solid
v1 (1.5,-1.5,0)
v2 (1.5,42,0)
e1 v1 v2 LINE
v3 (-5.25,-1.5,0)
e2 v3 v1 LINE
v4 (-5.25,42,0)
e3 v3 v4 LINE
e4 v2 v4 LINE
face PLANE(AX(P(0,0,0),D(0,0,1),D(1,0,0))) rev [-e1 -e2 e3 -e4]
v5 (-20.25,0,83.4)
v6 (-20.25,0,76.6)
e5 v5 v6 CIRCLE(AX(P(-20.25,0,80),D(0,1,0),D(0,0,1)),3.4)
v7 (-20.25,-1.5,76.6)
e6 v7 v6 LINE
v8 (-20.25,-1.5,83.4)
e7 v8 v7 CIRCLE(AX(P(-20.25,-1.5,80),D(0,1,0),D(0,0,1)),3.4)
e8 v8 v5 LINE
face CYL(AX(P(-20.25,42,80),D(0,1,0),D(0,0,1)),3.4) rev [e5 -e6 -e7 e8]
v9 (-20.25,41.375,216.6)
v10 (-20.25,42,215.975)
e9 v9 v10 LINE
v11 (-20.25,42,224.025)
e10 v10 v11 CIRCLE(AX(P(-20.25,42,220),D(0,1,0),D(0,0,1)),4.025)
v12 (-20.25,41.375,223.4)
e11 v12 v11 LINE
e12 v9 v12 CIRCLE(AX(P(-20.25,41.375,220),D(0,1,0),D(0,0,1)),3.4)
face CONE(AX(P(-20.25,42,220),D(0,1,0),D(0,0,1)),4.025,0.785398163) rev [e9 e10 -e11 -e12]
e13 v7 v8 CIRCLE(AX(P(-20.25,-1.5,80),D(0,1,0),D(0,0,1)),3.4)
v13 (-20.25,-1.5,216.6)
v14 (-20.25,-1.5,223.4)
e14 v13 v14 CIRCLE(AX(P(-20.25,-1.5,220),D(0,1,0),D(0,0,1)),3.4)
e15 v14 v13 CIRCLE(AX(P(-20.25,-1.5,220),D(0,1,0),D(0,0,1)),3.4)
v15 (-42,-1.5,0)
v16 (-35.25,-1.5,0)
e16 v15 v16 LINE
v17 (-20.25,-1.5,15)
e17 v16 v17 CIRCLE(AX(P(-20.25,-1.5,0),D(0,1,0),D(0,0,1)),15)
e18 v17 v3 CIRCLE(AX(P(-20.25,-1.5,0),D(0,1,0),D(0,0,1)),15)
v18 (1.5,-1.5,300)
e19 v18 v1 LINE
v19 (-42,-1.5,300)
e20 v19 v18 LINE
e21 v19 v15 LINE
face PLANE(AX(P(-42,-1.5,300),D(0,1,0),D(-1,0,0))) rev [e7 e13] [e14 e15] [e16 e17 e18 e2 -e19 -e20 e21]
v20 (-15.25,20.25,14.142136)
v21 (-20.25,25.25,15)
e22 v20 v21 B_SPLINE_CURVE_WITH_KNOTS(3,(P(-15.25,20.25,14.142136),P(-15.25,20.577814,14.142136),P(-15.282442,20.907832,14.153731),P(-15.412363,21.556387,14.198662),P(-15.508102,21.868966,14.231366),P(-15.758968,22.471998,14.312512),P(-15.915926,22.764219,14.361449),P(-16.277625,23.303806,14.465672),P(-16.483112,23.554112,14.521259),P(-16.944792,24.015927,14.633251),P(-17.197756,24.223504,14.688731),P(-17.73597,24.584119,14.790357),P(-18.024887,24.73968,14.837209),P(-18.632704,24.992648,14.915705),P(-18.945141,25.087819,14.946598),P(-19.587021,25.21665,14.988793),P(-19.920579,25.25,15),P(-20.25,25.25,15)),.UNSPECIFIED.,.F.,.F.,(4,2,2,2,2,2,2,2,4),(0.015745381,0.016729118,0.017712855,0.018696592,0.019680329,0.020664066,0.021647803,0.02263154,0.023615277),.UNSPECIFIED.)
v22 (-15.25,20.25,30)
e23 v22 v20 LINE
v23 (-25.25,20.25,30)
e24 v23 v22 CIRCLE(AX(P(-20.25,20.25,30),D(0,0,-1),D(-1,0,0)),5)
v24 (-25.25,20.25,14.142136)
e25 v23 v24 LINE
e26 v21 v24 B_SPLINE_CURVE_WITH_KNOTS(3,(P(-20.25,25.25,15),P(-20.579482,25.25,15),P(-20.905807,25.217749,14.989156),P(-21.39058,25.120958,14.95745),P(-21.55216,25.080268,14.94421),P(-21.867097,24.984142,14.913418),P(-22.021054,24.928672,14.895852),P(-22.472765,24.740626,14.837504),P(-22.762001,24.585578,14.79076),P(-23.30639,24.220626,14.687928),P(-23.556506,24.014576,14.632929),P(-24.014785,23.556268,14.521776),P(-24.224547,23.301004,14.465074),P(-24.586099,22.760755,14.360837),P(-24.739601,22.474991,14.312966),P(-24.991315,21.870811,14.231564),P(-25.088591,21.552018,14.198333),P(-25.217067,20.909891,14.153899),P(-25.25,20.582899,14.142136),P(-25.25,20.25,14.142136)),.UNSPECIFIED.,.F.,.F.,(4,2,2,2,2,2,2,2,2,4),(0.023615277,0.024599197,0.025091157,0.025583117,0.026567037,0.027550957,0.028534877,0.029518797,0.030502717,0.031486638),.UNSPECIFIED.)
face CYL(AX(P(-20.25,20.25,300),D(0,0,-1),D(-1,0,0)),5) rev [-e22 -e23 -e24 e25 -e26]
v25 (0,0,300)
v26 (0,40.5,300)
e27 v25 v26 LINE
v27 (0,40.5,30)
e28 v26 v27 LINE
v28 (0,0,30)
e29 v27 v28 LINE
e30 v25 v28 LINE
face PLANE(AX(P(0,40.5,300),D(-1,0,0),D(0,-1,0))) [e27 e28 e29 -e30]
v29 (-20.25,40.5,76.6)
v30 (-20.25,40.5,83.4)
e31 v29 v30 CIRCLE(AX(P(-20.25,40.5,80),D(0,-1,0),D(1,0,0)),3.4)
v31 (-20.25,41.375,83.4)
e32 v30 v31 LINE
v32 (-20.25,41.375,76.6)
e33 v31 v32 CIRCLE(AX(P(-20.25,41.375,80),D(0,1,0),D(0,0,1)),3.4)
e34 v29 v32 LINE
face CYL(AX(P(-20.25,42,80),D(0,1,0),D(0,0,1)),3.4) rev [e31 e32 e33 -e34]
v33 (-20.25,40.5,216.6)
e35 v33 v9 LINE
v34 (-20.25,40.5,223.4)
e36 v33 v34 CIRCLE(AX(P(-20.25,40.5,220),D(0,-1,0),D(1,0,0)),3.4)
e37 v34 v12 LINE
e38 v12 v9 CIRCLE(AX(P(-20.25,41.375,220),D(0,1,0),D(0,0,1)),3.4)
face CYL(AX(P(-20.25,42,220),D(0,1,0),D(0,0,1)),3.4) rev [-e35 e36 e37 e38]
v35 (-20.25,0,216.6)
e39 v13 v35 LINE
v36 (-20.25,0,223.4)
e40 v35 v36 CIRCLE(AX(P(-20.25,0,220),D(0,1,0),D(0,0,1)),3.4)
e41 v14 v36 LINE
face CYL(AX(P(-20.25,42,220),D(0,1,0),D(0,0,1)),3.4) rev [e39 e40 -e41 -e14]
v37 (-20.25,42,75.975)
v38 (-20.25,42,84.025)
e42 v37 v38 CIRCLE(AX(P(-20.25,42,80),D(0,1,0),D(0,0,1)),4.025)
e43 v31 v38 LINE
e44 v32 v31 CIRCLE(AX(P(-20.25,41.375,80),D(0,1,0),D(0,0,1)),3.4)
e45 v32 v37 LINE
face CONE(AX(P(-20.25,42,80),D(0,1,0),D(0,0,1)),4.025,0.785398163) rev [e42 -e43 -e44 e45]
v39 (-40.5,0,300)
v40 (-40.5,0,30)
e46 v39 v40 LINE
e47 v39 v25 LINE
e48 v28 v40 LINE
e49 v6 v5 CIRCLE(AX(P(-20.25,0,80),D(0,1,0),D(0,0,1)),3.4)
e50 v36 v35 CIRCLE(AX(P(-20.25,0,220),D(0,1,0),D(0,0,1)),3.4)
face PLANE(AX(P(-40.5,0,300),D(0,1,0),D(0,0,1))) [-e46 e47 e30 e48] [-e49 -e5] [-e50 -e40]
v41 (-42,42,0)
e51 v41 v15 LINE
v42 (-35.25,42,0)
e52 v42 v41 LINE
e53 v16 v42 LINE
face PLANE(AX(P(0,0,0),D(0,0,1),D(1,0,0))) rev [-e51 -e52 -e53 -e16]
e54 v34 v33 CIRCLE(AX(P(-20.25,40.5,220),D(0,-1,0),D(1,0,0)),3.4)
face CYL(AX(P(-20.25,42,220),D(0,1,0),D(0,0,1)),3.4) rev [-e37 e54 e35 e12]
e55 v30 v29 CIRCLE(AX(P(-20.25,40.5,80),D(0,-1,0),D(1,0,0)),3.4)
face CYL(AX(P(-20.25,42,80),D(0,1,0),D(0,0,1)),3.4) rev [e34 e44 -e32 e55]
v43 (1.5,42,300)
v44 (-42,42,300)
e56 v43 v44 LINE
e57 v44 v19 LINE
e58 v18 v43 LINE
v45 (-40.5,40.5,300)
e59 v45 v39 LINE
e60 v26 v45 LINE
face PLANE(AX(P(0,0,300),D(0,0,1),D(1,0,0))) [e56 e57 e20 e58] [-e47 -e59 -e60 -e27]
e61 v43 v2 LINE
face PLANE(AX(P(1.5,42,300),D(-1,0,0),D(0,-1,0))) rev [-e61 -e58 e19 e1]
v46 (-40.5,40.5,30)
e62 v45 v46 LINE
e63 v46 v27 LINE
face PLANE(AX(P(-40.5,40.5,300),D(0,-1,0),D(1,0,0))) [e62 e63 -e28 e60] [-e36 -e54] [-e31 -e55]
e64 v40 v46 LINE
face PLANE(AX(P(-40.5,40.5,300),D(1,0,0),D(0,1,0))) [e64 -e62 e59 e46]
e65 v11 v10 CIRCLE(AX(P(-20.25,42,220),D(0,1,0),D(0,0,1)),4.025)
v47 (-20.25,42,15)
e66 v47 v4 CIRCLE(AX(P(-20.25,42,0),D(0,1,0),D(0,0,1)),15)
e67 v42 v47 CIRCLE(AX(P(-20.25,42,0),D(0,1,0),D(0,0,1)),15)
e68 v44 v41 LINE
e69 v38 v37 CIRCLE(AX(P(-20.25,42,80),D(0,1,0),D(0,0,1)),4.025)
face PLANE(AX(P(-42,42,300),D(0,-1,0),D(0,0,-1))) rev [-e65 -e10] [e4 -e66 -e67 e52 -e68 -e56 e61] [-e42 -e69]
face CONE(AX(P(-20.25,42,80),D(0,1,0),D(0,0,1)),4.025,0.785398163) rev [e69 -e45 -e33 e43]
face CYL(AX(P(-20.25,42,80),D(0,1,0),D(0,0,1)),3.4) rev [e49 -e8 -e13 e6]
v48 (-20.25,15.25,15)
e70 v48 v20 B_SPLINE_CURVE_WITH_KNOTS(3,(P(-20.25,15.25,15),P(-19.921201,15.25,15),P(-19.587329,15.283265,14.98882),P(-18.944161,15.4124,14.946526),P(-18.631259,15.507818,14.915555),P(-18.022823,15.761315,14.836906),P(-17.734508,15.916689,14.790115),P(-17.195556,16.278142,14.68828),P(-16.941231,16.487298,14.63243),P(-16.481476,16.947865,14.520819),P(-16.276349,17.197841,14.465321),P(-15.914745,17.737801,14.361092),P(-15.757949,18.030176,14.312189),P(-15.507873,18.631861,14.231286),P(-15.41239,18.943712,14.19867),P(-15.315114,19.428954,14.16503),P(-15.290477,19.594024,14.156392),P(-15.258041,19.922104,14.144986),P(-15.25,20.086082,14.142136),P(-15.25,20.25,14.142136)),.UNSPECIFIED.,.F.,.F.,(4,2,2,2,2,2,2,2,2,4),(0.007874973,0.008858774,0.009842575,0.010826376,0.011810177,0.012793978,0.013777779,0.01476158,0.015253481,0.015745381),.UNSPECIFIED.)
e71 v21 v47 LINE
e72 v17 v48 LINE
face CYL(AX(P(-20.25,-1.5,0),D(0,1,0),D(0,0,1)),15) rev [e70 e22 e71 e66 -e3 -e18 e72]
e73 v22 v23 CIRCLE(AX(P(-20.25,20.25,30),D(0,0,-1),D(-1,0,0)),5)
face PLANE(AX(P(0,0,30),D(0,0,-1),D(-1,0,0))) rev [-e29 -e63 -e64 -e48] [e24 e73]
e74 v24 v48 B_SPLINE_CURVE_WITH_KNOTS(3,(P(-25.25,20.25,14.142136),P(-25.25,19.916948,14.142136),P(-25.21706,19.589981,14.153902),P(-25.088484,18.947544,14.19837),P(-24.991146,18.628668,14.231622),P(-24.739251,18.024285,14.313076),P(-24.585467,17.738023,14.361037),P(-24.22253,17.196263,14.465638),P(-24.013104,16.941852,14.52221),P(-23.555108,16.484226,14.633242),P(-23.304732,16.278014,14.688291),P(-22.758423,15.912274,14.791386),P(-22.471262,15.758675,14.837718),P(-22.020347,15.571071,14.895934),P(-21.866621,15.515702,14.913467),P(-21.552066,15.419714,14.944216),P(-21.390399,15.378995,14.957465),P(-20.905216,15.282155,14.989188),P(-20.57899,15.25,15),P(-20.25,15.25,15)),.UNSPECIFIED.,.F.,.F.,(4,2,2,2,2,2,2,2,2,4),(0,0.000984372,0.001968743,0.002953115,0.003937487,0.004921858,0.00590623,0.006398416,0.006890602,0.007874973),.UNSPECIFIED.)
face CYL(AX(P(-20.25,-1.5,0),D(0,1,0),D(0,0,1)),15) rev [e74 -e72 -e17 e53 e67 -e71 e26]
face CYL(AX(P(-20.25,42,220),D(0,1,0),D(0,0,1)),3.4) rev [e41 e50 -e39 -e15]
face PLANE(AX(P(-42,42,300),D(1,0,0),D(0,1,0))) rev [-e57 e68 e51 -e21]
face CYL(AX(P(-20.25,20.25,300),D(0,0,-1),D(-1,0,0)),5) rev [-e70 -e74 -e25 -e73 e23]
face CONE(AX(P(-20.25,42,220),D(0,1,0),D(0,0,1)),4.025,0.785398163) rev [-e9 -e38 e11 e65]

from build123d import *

# Parameters (mm, degrees)
SKETCH1_W                   = 43.5
SKETCH1_H                   = 43.5
SKETCH1_W_2                 = 40.5
SKETCH1_H_2                 = 40.5
BOSS_EXTRUDE1_DEPTH         = 300
SKETCH2_W                   = 43.5
SKETCH2_H                   = 43.5
BOSS_EXTRUDE2_DEPTH         = 30
M8_TAPPED_HOLE1_D           = 6.8
M8_TAPPED_HOLE1_CSINK_D     = 8.05
M8_TAPPED_HOLE1_CSINK_ANGLE = 90
CUT_EXTRUDE1_DEPTH          = 307.033086447
SKETCH6_R                   = 5
CUT_EXTRUDE2_DEPTH          = 306.823478497


with BuildPart() as part:
    # Sketch1 → Boss-Extrude1 (new body)
    with BuildSketch(Plane.XY):
        with Locations((-20.25, 20.25)):
            Rectangle(SKETCH1_W, SKETCH1_H)
        with Locations((-20.25, 20.25)):
            Rectangle(SKETCH1_W_2, SKETCH1_H_2, mode=Mode.SUBTRACT)
    extrude(amount=BOSS_EXTRUDE1_DEPTH)

    # Sketch2 → Boss-Extrude2 (add)
    with BuildSketch(Plane(origin=(0, 0, 0), x_dir=(-1, 0, 0), z_dir=(0, 0, -1))):
        with Locations((20.25, 20.25)):
            Rectangle(SKETCH2_W, SKETCH2_H)
    extrude(amount=-BOSS_EXTRUDE2_DEPTH)

    # M8 Tapped Hole1 (through all)
    with Locations(Plane(origin=(0, 42, 0), x_dir=(1, 0, 0), z_dir=(0, 1, 0))):
        with Locations((-20.25, -220), (-20.25, -80)):
            CounterSinkHole(M8_TAPPED_HOLE1_D / 2, M8_TAPPED_HOLE1_CSINK_D / 2, counter_sink_angle=M8_TAPPED_HOLE1_CSINK_ANGLE)

    # Sketch5 → Cut-Extrude1 (cut, through all)
    with BuildSketch(Plane(origin=(0, 42, 0), x_dir=(1, 0, 0), z_dir=(0, 1, 0))):
        with BuildLine():
            Line((-35.25, 0), (-5.25, 0))
            ThreePointArc((-5.25, 0), (-20.25, -15), (-35.25, 0))
        make_face()
    extrude(amount=-CUT_EXTRUDE1_DEPTH, mode=Mode.SUBTRACT)

    # Sketch6 → Cut-Extrude2 (cut, through all)
    with BuildSketch(Plane(origin=(0, 0, 0), x_dir=(-1, 0, 0), z_dir=(0, 0, -1))):
        with Locations((20.25, 20.25)):
            Circle(SKETCH6_R)
    extrude(amount=-CUT_EXTRUDE2_DEPTH, mode=Mode.SUBTRACT)


solid = part.part
